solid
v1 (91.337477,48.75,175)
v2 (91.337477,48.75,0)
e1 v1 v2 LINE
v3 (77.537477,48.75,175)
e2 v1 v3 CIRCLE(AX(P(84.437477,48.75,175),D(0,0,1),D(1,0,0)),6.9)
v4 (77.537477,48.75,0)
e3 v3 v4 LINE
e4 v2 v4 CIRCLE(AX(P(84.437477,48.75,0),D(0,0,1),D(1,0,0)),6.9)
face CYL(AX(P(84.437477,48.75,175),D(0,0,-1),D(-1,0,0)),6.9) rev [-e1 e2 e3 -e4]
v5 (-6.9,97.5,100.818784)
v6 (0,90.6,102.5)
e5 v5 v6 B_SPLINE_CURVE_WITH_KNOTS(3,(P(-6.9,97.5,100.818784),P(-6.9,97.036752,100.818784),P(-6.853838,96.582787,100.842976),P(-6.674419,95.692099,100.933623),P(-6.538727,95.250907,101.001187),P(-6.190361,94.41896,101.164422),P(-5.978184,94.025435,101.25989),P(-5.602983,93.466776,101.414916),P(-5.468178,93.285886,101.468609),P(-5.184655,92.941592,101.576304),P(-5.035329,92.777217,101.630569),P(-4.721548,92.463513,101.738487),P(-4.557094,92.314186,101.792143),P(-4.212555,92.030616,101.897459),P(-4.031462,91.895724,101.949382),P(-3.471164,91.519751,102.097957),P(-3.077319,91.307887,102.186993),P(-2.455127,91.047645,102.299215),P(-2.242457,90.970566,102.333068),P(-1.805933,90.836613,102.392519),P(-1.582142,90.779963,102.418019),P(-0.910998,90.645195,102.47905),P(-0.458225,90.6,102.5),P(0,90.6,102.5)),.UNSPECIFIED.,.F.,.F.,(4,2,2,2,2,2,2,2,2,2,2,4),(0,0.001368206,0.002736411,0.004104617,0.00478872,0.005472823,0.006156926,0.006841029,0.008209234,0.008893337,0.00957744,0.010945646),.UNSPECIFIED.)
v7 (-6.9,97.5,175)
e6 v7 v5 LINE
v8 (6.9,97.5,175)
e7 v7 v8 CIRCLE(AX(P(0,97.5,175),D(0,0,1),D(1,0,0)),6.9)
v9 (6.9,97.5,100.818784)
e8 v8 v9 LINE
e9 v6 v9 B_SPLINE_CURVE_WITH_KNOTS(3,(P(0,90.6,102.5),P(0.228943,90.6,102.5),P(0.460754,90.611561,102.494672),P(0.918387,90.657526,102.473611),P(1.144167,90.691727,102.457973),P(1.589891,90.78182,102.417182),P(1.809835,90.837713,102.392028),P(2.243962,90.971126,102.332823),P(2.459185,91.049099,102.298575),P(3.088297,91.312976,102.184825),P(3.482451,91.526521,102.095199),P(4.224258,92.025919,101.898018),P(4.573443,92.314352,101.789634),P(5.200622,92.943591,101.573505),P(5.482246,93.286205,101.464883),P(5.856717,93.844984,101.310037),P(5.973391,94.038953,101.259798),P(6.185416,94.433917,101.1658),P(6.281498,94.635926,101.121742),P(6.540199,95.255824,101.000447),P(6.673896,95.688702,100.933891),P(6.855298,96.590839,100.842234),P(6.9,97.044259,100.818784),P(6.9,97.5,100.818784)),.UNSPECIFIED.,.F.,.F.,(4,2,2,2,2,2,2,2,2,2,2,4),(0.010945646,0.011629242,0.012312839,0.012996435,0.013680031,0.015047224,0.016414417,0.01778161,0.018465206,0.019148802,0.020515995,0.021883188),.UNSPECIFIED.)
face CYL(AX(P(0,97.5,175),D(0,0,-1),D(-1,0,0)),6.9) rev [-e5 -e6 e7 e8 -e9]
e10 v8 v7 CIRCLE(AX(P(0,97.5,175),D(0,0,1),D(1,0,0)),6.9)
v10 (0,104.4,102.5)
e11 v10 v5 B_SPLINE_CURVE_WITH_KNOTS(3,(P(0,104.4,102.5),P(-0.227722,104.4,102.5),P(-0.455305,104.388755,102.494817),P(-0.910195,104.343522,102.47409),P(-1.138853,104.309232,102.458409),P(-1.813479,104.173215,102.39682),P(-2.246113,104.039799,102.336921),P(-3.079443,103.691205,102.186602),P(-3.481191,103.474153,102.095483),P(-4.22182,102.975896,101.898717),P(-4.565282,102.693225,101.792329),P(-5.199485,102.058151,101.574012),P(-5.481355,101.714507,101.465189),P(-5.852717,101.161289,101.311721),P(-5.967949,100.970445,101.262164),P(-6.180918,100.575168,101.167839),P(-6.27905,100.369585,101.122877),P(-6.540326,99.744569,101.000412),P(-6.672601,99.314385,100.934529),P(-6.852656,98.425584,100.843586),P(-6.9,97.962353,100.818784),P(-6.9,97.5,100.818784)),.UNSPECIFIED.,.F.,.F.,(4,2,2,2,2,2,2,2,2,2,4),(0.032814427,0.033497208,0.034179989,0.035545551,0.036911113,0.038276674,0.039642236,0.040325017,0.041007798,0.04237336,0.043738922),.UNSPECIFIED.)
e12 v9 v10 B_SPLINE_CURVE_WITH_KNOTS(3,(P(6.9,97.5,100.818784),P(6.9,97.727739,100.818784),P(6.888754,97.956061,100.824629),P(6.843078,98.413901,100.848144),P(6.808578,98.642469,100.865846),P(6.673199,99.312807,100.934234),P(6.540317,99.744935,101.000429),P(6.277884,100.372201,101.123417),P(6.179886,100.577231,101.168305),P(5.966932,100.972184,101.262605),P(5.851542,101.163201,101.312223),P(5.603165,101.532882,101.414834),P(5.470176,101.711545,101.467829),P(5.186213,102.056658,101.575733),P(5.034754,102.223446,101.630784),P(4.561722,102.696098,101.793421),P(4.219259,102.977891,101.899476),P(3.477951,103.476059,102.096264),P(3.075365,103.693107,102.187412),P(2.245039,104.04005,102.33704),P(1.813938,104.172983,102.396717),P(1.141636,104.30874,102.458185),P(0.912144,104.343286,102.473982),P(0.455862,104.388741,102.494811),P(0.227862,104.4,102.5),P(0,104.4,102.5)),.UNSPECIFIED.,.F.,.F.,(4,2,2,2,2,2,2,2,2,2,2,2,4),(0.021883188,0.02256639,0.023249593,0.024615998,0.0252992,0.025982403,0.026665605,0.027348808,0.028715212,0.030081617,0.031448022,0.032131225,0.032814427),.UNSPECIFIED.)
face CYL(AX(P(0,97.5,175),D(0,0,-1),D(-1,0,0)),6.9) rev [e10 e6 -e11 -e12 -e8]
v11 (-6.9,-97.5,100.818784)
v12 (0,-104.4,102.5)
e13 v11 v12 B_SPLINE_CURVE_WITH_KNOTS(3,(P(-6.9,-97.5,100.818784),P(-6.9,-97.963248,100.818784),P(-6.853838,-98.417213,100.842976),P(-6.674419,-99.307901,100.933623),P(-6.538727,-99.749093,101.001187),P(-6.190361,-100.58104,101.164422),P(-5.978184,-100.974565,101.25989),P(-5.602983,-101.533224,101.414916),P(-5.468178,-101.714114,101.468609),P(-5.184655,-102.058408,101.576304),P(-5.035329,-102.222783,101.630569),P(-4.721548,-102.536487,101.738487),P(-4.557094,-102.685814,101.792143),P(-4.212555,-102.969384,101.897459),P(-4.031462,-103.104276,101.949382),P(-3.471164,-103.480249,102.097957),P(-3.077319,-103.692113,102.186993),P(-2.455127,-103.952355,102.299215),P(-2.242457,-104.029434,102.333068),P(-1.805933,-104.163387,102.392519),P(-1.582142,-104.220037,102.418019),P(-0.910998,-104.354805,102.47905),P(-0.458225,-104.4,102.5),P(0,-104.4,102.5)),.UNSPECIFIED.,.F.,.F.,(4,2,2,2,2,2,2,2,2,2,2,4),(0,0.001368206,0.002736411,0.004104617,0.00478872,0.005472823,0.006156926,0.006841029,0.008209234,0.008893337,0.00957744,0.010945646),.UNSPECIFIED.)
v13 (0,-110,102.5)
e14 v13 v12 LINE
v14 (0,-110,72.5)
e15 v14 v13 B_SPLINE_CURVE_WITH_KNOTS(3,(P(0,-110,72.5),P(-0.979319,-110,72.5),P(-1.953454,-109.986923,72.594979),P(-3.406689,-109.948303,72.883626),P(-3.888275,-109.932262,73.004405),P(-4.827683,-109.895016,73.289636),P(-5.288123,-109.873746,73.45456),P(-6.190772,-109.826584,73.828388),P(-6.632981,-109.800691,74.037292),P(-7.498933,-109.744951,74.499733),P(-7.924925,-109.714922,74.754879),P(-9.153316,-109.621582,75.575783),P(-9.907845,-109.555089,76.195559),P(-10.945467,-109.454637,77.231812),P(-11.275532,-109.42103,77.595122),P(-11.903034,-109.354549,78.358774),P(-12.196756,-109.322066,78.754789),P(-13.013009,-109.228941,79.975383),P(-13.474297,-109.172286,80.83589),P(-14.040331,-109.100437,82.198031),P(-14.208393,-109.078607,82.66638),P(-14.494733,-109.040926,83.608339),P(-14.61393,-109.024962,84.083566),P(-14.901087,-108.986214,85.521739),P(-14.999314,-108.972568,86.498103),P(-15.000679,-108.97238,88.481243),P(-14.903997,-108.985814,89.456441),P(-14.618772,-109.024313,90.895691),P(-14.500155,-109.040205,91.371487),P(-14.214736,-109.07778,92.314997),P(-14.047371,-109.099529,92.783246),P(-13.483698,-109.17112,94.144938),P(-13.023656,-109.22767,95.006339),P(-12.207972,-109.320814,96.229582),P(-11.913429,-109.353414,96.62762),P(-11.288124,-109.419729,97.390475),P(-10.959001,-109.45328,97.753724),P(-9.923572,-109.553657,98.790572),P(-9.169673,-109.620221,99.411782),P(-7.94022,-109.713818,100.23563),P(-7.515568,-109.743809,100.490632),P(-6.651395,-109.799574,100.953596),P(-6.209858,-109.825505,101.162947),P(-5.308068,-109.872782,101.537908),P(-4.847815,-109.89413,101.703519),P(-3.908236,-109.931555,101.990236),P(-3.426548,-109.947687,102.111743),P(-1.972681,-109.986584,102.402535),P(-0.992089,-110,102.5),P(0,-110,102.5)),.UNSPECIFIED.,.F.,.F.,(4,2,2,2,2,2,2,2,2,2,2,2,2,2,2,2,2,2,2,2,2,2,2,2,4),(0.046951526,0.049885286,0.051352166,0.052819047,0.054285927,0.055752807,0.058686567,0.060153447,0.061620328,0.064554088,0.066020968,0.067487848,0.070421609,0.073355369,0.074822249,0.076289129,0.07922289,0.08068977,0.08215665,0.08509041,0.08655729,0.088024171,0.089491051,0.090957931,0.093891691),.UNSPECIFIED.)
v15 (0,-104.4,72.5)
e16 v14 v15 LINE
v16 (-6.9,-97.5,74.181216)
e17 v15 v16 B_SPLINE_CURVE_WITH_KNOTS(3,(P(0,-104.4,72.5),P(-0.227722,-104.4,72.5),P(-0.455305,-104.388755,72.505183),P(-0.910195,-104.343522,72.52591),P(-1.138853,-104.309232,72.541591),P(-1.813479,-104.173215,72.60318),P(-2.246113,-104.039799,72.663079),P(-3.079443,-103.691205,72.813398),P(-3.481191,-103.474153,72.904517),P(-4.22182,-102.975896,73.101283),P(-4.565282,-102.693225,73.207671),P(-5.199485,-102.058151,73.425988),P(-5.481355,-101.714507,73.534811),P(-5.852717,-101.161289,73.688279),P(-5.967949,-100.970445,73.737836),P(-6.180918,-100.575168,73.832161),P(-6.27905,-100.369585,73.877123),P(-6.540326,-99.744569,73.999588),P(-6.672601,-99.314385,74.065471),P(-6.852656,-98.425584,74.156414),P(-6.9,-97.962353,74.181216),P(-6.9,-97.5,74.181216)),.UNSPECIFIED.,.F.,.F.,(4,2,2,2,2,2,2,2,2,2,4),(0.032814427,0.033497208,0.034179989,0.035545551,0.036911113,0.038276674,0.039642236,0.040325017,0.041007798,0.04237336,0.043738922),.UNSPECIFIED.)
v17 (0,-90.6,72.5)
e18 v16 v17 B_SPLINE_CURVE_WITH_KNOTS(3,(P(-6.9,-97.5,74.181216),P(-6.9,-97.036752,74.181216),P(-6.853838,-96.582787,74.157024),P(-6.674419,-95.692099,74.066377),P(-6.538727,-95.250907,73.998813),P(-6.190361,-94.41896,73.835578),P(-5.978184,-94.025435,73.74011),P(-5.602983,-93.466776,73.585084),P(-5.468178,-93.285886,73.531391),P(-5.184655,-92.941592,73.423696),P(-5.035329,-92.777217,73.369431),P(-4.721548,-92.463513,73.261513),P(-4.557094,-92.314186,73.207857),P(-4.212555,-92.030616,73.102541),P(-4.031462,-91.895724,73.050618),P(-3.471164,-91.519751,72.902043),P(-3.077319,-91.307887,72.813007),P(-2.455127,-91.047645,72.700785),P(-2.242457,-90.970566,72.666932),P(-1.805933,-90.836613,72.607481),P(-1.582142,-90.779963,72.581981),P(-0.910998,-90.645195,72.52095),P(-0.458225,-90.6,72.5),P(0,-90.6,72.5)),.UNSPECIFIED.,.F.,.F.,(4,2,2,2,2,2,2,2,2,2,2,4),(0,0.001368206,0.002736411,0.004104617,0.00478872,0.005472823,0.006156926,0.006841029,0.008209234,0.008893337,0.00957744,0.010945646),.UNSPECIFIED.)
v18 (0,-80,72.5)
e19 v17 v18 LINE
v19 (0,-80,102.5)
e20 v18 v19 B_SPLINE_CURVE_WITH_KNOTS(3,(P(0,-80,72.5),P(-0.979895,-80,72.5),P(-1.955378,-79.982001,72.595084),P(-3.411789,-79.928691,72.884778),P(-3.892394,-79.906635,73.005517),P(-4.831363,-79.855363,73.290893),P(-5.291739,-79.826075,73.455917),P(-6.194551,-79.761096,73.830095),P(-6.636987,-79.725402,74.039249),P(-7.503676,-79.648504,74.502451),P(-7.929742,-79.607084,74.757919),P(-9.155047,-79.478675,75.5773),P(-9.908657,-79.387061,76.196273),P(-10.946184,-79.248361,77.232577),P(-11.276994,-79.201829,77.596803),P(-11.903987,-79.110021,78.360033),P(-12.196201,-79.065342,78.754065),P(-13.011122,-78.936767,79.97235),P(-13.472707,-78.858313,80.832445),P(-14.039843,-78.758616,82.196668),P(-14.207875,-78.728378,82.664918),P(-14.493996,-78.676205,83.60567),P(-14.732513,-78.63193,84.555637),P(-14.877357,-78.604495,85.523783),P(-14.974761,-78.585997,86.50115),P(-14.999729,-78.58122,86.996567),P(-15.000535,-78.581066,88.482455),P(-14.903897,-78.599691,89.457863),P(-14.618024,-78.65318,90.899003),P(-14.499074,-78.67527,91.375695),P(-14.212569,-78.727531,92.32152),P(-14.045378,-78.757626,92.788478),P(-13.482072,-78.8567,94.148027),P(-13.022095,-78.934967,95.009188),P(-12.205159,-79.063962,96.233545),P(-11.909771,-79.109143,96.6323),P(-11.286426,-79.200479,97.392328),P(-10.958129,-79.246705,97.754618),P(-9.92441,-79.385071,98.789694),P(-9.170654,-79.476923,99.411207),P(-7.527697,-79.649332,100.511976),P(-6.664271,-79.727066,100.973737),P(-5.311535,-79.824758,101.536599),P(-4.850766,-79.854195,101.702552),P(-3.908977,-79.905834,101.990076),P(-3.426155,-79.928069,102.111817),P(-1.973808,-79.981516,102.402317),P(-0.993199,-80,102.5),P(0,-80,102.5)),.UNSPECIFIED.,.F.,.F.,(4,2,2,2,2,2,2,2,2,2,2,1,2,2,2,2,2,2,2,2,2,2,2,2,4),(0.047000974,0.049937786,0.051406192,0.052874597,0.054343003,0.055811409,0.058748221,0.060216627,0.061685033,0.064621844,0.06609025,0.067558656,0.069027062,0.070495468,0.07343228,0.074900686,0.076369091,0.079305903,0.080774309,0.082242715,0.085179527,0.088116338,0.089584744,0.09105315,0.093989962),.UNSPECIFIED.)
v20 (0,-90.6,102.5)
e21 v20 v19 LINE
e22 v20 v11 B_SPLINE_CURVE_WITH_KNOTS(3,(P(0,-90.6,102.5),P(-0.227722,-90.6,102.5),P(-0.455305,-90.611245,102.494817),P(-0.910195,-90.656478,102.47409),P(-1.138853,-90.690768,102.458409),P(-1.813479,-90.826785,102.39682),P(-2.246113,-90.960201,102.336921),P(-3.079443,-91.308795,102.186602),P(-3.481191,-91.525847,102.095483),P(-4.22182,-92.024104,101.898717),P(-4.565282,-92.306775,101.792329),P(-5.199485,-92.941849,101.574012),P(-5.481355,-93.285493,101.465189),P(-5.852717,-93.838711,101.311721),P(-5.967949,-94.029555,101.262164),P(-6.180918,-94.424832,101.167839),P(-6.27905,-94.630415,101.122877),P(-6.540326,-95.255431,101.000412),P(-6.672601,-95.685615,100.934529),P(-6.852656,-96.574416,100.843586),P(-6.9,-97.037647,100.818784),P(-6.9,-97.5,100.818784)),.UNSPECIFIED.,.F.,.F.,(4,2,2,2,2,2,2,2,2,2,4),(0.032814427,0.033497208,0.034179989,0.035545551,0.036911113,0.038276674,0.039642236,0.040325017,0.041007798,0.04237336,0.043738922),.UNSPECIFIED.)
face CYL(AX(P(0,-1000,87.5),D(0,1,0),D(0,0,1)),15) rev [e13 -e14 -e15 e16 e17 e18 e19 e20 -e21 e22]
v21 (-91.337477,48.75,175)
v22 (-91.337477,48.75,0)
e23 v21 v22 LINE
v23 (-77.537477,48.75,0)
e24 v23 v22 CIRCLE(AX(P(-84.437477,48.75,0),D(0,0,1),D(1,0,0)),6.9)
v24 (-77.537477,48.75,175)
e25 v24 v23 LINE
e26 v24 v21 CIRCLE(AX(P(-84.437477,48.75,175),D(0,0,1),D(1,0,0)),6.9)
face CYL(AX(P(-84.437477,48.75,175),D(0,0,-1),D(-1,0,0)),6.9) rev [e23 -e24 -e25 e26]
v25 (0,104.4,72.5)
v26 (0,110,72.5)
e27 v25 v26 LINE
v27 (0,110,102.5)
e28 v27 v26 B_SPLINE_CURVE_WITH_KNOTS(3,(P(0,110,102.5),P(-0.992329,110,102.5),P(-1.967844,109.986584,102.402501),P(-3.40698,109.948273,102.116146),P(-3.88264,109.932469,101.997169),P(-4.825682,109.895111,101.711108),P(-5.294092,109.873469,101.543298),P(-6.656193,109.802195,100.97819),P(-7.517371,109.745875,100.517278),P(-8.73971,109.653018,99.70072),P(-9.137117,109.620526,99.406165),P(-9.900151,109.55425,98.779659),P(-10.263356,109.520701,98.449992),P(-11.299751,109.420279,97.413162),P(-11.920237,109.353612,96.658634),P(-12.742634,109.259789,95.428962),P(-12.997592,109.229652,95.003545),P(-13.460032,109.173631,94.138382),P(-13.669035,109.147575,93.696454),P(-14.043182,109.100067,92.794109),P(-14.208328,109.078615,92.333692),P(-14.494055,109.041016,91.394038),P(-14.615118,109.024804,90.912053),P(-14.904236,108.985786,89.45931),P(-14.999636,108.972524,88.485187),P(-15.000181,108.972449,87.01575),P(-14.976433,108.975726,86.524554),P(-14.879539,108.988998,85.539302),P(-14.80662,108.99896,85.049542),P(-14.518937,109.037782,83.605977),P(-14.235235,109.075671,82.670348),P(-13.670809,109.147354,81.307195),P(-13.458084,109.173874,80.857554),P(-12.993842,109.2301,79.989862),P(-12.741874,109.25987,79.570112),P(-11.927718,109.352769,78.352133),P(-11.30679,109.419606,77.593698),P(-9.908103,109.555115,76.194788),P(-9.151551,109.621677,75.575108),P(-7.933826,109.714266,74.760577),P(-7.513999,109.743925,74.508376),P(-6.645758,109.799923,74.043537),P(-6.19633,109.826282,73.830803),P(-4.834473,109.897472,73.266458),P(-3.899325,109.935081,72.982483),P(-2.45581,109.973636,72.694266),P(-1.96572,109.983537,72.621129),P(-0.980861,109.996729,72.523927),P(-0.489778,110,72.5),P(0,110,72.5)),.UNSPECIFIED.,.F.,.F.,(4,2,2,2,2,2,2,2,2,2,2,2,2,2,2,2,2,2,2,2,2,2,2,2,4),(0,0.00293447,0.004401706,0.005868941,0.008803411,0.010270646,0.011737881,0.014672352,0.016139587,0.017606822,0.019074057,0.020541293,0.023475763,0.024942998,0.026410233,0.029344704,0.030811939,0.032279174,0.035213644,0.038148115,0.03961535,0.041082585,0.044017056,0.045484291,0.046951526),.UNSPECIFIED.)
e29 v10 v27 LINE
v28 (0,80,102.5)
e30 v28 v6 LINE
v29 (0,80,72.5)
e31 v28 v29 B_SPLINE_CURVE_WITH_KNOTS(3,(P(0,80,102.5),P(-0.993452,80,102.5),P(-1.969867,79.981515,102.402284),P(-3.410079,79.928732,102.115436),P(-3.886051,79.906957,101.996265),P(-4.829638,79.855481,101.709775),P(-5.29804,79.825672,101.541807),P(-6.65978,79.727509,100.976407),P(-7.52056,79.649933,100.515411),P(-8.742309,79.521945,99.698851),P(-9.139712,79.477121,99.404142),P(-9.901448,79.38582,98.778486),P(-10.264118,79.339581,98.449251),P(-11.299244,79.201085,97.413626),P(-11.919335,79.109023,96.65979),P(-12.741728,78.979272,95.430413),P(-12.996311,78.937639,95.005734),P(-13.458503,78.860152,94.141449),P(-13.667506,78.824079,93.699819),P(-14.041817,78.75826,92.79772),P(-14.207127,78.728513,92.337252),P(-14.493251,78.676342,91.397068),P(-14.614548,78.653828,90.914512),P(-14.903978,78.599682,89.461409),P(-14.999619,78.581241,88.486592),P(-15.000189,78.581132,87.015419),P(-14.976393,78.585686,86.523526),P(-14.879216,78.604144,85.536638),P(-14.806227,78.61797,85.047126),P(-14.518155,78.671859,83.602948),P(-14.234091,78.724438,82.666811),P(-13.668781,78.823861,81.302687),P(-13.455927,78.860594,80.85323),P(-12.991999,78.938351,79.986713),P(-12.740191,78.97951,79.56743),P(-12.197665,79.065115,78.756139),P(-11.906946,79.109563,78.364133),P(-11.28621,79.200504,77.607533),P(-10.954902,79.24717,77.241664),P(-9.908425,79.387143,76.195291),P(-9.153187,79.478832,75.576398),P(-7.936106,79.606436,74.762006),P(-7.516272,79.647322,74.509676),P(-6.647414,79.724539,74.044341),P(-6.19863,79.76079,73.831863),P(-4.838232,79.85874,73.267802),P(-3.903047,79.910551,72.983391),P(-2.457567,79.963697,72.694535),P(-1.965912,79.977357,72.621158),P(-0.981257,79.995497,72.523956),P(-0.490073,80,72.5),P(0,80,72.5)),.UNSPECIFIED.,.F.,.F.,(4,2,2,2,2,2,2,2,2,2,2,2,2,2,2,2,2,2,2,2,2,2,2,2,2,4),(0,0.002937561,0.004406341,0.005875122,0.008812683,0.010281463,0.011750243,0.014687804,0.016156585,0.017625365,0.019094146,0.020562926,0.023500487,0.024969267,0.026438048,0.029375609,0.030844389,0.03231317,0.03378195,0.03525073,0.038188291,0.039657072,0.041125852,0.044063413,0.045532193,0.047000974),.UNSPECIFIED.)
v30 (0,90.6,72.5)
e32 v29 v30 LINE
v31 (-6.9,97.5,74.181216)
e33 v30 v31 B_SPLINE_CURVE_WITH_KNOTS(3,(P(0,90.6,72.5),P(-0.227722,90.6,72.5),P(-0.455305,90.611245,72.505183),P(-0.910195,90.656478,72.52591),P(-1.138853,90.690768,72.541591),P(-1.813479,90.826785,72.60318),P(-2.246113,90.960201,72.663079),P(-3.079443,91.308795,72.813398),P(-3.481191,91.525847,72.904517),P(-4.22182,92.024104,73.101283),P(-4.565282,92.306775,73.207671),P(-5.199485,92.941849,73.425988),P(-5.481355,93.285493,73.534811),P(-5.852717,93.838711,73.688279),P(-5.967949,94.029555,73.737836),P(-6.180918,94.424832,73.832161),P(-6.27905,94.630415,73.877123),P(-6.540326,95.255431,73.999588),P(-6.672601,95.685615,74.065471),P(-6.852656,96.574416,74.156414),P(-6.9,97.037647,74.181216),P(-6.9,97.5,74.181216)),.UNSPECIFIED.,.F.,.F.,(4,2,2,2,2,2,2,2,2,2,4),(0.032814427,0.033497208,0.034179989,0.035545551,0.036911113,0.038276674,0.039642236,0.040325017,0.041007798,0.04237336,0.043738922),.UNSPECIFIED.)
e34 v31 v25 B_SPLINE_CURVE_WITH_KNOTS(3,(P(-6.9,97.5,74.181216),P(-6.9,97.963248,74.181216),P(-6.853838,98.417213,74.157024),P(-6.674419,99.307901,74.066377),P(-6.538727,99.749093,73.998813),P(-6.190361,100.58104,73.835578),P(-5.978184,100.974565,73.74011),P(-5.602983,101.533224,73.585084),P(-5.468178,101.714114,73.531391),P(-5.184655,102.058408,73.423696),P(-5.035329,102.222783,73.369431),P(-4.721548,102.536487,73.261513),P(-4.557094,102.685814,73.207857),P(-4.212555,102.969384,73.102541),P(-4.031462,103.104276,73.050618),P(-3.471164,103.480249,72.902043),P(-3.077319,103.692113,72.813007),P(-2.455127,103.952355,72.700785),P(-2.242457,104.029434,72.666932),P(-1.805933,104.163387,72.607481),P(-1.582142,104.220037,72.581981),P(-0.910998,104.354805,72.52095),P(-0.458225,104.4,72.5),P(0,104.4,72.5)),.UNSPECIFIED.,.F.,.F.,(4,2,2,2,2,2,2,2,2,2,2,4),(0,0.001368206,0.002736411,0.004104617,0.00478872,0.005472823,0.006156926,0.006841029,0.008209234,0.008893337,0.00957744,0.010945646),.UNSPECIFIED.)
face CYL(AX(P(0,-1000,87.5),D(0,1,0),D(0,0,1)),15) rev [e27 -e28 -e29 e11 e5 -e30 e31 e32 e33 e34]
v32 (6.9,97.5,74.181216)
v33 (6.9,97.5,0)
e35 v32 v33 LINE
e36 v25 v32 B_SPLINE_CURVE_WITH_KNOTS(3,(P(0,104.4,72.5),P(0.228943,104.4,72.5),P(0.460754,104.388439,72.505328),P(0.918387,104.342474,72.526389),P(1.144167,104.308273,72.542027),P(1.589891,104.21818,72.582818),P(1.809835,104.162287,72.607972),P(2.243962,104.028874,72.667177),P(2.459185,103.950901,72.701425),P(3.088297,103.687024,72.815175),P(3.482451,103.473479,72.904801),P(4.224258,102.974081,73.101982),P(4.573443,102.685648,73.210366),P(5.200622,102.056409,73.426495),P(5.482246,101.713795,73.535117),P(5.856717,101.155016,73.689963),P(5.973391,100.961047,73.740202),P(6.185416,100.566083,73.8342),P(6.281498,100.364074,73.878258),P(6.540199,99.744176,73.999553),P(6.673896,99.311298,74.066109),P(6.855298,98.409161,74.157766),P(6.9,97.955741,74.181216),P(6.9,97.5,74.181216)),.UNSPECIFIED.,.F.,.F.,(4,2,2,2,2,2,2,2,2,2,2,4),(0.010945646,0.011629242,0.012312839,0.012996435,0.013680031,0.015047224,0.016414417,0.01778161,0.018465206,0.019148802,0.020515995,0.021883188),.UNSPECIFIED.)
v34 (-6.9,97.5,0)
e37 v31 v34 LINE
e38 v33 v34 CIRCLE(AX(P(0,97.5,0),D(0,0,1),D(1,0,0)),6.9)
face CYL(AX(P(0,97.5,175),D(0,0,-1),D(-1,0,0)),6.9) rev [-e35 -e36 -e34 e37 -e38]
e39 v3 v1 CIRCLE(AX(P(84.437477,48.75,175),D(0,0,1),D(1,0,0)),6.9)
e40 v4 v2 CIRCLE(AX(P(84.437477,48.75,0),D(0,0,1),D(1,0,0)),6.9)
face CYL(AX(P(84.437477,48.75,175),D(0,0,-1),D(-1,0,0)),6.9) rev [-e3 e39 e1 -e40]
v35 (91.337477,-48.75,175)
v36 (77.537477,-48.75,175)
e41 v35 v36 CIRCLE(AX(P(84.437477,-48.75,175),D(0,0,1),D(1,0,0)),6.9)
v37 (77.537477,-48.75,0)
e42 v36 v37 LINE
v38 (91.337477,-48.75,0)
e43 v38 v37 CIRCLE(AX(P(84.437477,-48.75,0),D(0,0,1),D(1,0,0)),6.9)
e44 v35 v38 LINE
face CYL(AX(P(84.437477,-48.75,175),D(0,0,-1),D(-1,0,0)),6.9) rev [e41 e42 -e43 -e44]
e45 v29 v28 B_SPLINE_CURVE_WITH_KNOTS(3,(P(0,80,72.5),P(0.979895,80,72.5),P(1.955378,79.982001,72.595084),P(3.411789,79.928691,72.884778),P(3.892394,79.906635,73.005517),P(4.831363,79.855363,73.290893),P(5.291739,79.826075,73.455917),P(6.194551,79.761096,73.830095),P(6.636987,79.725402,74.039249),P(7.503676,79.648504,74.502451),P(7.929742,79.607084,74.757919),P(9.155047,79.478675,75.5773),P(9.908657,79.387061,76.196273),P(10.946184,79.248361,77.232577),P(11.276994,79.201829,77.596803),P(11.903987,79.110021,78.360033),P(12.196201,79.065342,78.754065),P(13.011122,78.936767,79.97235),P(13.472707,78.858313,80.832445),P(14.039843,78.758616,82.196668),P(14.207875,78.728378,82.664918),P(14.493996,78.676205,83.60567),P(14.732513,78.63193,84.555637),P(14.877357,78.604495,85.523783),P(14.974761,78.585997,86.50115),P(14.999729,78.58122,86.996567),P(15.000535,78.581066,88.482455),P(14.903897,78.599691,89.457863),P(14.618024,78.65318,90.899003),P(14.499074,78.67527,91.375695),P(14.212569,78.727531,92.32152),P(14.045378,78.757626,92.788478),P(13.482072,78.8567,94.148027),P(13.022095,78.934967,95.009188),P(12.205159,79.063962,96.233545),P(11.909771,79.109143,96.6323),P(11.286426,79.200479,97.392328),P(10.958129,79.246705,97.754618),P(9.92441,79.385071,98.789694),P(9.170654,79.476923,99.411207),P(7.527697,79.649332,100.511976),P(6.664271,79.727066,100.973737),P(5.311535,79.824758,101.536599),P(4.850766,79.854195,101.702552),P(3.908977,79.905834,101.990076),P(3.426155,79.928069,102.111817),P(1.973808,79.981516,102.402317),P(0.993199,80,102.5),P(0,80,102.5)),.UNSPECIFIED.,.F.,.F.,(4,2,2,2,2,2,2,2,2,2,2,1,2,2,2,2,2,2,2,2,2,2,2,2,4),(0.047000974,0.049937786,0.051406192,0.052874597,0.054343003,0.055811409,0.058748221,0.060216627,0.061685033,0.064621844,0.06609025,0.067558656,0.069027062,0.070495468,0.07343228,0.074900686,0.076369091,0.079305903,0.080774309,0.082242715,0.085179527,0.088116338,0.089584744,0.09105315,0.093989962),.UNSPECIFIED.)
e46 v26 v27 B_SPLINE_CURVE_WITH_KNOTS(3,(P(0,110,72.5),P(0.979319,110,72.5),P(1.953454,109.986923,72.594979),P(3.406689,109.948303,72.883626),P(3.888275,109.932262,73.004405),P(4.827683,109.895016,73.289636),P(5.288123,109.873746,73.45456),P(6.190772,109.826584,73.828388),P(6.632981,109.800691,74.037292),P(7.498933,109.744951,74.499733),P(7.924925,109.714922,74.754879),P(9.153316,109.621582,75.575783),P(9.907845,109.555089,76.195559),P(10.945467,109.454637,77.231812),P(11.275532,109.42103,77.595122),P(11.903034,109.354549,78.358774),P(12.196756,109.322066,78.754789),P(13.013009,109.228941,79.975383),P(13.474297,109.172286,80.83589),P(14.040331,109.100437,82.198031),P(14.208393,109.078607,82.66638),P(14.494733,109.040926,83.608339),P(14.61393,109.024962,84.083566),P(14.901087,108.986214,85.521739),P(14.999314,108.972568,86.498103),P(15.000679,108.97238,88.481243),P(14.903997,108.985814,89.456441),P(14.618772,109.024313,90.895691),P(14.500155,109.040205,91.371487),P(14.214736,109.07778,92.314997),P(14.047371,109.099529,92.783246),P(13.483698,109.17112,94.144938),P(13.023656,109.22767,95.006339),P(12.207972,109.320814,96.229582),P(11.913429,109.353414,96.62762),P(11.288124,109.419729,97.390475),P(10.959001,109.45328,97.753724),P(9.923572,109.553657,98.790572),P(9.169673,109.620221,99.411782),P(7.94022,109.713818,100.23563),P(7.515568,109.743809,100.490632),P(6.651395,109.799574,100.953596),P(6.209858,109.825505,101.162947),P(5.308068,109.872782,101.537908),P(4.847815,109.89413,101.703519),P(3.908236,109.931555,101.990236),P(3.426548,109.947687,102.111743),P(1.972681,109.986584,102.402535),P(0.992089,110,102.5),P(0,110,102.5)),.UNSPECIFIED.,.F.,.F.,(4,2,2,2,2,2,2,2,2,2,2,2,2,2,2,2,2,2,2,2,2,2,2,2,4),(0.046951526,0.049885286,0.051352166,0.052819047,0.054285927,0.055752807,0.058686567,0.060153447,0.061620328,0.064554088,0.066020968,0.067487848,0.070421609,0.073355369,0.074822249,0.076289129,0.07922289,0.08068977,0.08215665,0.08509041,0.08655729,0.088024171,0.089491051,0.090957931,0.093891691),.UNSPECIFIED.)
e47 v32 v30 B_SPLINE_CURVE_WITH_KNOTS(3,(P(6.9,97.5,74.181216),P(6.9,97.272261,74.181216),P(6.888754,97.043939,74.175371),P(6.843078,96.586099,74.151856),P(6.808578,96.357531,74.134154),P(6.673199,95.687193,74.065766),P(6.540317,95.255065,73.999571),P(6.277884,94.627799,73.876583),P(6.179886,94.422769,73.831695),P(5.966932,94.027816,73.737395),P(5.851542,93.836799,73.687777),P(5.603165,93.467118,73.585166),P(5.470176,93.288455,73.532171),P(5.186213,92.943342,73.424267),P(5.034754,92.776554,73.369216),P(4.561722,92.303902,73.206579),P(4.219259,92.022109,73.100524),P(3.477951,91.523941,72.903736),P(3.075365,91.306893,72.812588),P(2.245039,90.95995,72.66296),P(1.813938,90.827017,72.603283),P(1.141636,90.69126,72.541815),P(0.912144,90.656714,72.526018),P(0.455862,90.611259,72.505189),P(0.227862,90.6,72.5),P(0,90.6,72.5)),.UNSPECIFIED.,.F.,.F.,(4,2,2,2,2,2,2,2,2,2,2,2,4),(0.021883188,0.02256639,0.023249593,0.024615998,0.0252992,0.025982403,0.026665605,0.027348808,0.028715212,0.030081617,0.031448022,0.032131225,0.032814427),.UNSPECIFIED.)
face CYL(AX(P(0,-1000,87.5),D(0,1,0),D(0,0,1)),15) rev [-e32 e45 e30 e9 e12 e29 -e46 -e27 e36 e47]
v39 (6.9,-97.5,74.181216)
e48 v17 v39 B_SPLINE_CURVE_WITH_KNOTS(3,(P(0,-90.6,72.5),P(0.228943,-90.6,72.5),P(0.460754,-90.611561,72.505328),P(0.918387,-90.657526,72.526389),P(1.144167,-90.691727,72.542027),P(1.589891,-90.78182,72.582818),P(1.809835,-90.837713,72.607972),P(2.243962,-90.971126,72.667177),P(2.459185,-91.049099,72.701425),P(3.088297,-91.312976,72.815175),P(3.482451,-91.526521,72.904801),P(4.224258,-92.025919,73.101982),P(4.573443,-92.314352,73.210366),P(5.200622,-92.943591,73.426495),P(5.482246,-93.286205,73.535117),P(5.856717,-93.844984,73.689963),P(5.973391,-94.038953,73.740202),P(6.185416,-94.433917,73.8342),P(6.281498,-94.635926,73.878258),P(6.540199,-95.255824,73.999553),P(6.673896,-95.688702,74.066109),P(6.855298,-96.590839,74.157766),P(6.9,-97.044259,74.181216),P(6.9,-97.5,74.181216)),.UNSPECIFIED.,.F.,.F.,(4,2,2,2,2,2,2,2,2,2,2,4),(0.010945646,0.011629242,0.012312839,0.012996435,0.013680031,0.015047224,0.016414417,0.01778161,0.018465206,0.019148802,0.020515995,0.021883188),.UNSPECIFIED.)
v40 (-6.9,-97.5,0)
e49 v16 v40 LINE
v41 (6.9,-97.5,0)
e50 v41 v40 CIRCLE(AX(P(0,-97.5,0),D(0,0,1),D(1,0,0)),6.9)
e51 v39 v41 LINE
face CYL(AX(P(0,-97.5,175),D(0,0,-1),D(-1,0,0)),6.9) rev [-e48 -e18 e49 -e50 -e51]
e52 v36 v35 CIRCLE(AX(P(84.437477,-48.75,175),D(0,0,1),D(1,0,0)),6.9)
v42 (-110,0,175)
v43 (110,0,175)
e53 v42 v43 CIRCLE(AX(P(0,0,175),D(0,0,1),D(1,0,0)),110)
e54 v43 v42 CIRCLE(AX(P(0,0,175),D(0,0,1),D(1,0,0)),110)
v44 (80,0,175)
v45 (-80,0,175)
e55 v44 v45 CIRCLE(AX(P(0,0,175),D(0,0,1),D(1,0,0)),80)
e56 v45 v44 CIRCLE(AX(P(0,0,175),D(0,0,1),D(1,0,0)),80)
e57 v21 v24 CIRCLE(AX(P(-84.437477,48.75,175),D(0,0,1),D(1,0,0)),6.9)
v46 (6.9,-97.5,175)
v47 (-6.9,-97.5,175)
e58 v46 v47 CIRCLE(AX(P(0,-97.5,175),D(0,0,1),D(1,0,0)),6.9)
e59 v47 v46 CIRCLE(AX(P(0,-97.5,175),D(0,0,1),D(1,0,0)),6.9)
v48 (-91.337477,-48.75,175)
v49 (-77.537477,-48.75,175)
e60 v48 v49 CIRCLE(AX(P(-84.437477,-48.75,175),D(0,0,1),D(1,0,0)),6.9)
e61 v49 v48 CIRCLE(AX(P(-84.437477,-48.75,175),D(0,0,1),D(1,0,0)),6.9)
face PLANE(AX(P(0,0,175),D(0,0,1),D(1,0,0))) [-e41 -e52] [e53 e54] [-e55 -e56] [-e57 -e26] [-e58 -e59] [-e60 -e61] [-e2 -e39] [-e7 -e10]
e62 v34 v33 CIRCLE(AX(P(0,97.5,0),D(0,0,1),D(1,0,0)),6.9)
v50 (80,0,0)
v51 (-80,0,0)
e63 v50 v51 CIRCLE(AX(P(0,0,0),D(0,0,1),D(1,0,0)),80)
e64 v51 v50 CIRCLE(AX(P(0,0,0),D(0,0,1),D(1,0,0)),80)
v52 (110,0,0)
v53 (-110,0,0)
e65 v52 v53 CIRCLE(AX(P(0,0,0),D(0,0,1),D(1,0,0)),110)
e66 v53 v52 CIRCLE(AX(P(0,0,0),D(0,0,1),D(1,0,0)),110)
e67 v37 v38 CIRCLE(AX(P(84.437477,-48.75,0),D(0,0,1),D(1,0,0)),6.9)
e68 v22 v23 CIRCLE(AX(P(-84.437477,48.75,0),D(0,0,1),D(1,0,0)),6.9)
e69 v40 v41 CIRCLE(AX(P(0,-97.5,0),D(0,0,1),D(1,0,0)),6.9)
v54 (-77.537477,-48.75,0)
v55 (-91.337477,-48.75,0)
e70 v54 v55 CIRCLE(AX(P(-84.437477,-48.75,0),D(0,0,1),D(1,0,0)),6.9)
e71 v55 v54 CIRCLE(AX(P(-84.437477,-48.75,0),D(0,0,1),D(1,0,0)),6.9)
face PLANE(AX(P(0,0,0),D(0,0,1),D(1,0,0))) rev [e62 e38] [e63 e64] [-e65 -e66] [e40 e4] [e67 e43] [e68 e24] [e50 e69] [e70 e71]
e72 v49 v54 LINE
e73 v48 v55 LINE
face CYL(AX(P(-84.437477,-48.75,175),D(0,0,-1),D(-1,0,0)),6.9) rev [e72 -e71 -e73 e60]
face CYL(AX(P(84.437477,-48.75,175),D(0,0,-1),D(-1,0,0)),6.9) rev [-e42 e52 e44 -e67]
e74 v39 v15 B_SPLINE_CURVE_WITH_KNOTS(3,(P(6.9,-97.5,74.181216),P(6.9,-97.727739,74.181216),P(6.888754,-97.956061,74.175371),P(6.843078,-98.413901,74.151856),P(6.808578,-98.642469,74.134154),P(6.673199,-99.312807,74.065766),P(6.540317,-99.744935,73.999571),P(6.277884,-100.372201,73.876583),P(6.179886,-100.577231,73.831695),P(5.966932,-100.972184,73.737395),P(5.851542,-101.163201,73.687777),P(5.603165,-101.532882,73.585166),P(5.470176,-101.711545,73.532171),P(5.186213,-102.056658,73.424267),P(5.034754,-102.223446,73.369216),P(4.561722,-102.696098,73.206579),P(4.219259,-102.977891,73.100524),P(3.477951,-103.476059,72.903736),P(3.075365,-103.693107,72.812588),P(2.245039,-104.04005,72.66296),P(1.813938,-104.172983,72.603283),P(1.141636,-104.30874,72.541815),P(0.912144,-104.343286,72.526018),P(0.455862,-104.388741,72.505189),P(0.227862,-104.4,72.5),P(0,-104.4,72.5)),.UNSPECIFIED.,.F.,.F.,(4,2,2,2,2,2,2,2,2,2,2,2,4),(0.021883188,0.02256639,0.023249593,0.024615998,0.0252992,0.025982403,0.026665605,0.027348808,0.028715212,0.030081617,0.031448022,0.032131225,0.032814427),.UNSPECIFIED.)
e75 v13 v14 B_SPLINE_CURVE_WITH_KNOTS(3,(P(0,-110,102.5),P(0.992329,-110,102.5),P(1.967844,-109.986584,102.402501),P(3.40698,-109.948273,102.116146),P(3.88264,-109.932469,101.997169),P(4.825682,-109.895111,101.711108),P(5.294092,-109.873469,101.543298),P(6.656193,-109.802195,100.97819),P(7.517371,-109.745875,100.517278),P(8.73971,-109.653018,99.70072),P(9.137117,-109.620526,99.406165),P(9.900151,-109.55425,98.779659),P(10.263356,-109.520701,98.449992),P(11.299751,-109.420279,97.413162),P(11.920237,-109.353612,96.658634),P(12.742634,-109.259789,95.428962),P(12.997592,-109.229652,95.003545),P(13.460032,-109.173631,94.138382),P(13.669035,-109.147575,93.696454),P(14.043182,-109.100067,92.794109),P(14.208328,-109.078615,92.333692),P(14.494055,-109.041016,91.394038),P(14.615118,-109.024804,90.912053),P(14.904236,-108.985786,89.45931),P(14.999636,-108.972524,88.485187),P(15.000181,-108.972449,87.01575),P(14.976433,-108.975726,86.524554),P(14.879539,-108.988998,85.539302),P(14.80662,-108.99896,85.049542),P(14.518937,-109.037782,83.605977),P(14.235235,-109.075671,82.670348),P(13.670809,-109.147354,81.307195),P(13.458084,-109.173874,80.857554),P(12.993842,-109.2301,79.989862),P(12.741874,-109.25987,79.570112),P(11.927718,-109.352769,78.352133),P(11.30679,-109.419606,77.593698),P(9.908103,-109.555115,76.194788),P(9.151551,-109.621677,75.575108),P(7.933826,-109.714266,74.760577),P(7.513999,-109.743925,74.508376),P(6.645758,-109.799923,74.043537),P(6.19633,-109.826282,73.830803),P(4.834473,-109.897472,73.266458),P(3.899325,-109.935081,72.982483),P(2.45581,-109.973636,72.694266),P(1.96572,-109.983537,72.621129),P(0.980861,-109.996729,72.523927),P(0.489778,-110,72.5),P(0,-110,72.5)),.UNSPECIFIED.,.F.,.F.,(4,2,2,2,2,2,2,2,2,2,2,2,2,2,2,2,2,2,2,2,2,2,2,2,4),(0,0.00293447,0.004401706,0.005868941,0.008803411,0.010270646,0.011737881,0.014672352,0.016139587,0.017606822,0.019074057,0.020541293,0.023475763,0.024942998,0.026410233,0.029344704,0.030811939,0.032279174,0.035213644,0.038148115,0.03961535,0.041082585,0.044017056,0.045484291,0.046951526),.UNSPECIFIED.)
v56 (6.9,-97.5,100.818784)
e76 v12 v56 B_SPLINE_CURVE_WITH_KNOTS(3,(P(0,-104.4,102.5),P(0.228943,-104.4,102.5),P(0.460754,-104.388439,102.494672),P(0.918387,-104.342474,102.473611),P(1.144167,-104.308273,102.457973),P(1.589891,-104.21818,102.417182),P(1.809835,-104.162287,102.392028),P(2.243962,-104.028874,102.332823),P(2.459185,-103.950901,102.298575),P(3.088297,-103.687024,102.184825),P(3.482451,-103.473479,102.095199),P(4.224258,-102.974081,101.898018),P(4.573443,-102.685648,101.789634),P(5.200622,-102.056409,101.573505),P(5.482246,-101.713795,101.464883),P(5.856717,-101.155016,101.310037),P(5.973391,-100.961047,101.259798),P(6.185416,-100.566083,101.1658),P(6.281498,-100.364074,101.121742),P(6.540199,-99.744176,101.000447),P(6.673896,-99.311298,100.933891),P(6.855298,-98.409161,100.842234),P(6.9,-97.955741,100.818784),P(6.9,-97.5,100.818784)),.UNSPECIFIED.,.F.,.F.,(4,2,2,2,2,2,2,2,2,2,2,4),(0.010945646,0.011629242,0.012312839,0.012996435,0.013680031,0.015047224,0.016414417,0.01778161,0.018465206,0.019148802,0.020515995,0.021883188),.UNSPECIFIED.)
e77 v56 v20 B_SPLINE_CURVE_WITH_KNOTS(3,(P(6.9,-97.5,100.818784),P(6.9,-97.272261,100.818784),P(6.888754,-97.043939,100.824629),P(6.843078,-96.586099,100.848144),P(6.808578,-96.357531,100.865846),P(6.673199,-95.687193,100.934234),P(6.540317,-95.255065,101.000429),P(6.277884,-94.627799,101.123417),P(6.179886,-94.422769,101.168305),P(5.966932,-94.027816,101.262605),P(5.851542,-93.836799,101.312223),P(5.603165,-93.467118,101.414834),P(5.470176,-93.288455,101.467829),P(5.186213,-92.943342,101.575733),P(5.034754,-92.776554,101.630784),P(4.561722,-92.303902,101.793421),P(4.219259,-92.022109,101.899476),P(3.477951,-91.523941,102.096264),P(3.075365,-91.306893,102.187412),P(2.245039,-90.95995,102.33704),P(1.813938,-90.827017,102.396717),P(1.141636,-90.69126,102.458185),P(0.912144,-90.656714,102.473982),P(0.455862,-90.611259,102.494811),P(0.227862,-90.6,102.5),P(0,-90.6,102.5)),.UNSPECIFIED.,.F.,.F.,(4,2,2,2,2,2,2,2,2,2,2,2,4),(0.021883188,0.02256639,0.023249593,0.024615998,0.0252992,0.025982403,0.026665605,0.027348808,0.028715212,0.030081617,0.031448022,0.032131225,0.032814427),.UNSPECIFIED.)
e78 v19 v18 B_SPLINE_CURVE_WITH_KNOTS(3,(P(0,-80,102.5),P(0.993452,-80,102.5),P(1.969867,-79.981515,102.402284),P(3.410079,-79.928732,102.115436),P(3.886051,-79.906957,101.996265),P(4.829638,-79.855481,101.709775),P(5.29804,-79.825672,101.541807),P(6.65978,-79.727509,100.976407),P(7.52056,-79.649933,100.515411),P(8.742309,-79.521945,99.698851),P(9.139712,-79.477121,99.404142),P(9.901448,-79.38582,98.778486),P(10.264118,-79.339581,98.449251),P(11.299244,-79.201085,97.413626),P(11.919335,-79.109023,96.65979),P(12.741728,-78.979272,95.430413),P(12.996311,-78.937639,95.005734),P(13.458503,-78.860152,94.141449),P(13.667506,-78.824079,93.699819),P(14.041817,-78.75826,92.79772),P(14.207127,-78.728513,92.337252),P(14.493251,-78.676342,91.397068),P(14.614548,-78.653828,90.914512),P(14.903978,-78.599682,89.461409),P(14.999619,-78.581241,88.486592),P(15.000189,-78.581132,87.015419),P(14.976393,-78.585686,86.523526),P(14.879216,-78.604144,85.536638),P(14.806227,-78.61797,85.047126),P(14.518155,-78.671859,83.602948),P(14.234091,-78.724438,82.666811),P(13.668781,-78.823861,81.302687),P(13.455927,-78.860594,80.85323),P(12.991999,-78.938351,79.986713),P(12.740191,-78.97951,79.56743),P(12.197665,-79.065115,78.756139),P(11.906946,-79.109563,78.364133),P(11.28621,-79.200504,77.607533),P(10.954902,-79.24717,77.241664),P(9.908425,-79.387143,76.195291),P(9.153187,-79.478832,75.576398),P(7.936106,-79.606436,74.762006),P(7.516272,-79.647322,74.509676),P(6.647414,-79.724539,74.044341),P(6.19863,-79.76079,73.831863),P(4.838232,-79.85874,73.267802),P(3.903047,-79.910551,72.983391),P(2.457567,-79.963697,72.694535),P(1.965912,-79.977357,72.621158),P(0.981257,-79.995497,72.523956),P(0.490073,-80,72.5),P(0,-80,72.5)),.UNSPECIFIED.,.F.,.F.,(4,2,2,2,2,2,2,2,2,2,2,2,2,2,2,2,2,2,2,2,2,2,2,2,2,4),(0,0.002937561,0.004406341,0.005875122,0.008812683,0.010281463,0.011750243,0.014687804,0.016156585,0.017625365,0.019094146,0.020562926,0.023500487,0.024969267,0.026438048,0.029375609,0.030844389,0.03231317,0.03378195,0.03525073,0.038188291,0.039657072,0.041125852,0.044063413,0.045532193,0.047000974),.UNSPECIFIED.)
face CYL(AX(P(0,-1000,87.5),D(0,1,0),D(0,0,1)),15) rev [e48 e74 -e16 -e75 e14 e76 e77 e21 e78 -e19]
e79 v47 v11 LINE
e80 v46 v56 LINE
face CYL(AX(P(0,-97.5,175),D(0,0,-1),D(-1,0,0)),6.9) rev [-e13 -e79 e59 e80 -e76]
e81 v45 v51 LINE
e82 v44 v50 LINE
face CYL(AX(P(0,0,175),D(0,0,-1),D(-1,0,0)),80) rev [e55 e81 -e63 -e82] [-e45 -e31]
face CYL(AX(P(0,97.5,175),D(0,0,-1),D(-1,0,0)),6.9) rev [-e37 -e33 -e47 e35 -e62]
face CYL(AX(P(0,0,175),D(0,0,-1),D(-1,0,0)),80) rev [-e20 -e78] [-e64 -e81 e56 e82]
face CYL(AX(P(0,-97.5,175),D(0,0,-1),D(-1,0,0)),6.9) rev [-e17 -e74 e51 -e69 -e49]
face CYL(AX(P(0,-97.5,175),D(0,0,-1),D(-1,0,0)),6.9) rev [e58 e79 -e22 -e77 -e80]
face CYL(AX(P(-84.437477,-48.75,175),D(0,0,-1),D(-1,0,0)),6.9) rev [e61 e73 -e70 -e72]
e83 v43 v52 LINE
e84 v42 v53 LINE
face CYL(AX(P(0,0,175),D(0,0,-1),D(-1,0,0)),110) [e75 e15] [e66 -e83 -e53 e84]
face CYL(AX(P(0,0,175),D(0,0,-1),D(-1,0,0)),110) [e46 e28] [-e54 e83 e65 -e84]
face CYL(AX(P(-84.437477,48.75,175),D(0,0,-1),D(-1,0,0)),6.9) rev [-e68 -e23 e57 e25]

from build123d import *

# Parameters (mm, degrees)
SKETCH1_R           = 110
SKETCH1_R_2         = 80
SKETCH1_R_3         = 6.9
BOSS_EXTRUDE1_DEPTH = 175
SKETCH2_R           = 15
CUT_EXTRUDE1_DEPTH  = 1000


with BuildPart() as part:
    # Sketch1 → Boss-Extrude1 (new body)
    with BuildSketch(Plane.XY):
        Circle(SKETCH1_R)
        Circle(SKETCH1_R_2, mode=Mode.SUBTRACT)
        with Locations((0, 97.5)):
            Circle(SKETCH1_R_3, mode=Mode.SUBTRACT)
        with Locations((84.437476869, 48.75)):
            Circle(SKETCH1_R_3, mode=Mode.SUBTRACT)
        with Locations((84.437476869, -48.75)):
            Circle(SKETCH1_R_3, mode=Mode.SUBTRACT)
        with Locations((0, -97.5)):
            Circle(SKETCH1_R_3, mode=Mode.SUBTRACT)
        with Locations((-84.437476869, -48.75)):
            Circle(SKETCH1_R_3, mode=Mode.SUBTRACT)
        with Locations((-84.437476869, 48.75)):
            Circle(SKETCH1_R_3, mode=Mode.SUBTRACT)
    extrude(amount=BOSS_EXTRUDE1_DEPTH)

    # Sketch2 → Cut-Extrude1 (cut, symmetric)
    with BuildSketch(Plane(origin=(0, 0, 0), x_dir=(1, 0, 0), z_dir=(0, 1, 0))):
        with Locations(Location((0, -87.5, 0), (0, 0, 270))):
            Circle(SKETCH2_R)
    extrude(amount=CUT_EXTRUDE1_DEPTH, both=True, mode=Mode.SUBTRACT)


solid = part.part
